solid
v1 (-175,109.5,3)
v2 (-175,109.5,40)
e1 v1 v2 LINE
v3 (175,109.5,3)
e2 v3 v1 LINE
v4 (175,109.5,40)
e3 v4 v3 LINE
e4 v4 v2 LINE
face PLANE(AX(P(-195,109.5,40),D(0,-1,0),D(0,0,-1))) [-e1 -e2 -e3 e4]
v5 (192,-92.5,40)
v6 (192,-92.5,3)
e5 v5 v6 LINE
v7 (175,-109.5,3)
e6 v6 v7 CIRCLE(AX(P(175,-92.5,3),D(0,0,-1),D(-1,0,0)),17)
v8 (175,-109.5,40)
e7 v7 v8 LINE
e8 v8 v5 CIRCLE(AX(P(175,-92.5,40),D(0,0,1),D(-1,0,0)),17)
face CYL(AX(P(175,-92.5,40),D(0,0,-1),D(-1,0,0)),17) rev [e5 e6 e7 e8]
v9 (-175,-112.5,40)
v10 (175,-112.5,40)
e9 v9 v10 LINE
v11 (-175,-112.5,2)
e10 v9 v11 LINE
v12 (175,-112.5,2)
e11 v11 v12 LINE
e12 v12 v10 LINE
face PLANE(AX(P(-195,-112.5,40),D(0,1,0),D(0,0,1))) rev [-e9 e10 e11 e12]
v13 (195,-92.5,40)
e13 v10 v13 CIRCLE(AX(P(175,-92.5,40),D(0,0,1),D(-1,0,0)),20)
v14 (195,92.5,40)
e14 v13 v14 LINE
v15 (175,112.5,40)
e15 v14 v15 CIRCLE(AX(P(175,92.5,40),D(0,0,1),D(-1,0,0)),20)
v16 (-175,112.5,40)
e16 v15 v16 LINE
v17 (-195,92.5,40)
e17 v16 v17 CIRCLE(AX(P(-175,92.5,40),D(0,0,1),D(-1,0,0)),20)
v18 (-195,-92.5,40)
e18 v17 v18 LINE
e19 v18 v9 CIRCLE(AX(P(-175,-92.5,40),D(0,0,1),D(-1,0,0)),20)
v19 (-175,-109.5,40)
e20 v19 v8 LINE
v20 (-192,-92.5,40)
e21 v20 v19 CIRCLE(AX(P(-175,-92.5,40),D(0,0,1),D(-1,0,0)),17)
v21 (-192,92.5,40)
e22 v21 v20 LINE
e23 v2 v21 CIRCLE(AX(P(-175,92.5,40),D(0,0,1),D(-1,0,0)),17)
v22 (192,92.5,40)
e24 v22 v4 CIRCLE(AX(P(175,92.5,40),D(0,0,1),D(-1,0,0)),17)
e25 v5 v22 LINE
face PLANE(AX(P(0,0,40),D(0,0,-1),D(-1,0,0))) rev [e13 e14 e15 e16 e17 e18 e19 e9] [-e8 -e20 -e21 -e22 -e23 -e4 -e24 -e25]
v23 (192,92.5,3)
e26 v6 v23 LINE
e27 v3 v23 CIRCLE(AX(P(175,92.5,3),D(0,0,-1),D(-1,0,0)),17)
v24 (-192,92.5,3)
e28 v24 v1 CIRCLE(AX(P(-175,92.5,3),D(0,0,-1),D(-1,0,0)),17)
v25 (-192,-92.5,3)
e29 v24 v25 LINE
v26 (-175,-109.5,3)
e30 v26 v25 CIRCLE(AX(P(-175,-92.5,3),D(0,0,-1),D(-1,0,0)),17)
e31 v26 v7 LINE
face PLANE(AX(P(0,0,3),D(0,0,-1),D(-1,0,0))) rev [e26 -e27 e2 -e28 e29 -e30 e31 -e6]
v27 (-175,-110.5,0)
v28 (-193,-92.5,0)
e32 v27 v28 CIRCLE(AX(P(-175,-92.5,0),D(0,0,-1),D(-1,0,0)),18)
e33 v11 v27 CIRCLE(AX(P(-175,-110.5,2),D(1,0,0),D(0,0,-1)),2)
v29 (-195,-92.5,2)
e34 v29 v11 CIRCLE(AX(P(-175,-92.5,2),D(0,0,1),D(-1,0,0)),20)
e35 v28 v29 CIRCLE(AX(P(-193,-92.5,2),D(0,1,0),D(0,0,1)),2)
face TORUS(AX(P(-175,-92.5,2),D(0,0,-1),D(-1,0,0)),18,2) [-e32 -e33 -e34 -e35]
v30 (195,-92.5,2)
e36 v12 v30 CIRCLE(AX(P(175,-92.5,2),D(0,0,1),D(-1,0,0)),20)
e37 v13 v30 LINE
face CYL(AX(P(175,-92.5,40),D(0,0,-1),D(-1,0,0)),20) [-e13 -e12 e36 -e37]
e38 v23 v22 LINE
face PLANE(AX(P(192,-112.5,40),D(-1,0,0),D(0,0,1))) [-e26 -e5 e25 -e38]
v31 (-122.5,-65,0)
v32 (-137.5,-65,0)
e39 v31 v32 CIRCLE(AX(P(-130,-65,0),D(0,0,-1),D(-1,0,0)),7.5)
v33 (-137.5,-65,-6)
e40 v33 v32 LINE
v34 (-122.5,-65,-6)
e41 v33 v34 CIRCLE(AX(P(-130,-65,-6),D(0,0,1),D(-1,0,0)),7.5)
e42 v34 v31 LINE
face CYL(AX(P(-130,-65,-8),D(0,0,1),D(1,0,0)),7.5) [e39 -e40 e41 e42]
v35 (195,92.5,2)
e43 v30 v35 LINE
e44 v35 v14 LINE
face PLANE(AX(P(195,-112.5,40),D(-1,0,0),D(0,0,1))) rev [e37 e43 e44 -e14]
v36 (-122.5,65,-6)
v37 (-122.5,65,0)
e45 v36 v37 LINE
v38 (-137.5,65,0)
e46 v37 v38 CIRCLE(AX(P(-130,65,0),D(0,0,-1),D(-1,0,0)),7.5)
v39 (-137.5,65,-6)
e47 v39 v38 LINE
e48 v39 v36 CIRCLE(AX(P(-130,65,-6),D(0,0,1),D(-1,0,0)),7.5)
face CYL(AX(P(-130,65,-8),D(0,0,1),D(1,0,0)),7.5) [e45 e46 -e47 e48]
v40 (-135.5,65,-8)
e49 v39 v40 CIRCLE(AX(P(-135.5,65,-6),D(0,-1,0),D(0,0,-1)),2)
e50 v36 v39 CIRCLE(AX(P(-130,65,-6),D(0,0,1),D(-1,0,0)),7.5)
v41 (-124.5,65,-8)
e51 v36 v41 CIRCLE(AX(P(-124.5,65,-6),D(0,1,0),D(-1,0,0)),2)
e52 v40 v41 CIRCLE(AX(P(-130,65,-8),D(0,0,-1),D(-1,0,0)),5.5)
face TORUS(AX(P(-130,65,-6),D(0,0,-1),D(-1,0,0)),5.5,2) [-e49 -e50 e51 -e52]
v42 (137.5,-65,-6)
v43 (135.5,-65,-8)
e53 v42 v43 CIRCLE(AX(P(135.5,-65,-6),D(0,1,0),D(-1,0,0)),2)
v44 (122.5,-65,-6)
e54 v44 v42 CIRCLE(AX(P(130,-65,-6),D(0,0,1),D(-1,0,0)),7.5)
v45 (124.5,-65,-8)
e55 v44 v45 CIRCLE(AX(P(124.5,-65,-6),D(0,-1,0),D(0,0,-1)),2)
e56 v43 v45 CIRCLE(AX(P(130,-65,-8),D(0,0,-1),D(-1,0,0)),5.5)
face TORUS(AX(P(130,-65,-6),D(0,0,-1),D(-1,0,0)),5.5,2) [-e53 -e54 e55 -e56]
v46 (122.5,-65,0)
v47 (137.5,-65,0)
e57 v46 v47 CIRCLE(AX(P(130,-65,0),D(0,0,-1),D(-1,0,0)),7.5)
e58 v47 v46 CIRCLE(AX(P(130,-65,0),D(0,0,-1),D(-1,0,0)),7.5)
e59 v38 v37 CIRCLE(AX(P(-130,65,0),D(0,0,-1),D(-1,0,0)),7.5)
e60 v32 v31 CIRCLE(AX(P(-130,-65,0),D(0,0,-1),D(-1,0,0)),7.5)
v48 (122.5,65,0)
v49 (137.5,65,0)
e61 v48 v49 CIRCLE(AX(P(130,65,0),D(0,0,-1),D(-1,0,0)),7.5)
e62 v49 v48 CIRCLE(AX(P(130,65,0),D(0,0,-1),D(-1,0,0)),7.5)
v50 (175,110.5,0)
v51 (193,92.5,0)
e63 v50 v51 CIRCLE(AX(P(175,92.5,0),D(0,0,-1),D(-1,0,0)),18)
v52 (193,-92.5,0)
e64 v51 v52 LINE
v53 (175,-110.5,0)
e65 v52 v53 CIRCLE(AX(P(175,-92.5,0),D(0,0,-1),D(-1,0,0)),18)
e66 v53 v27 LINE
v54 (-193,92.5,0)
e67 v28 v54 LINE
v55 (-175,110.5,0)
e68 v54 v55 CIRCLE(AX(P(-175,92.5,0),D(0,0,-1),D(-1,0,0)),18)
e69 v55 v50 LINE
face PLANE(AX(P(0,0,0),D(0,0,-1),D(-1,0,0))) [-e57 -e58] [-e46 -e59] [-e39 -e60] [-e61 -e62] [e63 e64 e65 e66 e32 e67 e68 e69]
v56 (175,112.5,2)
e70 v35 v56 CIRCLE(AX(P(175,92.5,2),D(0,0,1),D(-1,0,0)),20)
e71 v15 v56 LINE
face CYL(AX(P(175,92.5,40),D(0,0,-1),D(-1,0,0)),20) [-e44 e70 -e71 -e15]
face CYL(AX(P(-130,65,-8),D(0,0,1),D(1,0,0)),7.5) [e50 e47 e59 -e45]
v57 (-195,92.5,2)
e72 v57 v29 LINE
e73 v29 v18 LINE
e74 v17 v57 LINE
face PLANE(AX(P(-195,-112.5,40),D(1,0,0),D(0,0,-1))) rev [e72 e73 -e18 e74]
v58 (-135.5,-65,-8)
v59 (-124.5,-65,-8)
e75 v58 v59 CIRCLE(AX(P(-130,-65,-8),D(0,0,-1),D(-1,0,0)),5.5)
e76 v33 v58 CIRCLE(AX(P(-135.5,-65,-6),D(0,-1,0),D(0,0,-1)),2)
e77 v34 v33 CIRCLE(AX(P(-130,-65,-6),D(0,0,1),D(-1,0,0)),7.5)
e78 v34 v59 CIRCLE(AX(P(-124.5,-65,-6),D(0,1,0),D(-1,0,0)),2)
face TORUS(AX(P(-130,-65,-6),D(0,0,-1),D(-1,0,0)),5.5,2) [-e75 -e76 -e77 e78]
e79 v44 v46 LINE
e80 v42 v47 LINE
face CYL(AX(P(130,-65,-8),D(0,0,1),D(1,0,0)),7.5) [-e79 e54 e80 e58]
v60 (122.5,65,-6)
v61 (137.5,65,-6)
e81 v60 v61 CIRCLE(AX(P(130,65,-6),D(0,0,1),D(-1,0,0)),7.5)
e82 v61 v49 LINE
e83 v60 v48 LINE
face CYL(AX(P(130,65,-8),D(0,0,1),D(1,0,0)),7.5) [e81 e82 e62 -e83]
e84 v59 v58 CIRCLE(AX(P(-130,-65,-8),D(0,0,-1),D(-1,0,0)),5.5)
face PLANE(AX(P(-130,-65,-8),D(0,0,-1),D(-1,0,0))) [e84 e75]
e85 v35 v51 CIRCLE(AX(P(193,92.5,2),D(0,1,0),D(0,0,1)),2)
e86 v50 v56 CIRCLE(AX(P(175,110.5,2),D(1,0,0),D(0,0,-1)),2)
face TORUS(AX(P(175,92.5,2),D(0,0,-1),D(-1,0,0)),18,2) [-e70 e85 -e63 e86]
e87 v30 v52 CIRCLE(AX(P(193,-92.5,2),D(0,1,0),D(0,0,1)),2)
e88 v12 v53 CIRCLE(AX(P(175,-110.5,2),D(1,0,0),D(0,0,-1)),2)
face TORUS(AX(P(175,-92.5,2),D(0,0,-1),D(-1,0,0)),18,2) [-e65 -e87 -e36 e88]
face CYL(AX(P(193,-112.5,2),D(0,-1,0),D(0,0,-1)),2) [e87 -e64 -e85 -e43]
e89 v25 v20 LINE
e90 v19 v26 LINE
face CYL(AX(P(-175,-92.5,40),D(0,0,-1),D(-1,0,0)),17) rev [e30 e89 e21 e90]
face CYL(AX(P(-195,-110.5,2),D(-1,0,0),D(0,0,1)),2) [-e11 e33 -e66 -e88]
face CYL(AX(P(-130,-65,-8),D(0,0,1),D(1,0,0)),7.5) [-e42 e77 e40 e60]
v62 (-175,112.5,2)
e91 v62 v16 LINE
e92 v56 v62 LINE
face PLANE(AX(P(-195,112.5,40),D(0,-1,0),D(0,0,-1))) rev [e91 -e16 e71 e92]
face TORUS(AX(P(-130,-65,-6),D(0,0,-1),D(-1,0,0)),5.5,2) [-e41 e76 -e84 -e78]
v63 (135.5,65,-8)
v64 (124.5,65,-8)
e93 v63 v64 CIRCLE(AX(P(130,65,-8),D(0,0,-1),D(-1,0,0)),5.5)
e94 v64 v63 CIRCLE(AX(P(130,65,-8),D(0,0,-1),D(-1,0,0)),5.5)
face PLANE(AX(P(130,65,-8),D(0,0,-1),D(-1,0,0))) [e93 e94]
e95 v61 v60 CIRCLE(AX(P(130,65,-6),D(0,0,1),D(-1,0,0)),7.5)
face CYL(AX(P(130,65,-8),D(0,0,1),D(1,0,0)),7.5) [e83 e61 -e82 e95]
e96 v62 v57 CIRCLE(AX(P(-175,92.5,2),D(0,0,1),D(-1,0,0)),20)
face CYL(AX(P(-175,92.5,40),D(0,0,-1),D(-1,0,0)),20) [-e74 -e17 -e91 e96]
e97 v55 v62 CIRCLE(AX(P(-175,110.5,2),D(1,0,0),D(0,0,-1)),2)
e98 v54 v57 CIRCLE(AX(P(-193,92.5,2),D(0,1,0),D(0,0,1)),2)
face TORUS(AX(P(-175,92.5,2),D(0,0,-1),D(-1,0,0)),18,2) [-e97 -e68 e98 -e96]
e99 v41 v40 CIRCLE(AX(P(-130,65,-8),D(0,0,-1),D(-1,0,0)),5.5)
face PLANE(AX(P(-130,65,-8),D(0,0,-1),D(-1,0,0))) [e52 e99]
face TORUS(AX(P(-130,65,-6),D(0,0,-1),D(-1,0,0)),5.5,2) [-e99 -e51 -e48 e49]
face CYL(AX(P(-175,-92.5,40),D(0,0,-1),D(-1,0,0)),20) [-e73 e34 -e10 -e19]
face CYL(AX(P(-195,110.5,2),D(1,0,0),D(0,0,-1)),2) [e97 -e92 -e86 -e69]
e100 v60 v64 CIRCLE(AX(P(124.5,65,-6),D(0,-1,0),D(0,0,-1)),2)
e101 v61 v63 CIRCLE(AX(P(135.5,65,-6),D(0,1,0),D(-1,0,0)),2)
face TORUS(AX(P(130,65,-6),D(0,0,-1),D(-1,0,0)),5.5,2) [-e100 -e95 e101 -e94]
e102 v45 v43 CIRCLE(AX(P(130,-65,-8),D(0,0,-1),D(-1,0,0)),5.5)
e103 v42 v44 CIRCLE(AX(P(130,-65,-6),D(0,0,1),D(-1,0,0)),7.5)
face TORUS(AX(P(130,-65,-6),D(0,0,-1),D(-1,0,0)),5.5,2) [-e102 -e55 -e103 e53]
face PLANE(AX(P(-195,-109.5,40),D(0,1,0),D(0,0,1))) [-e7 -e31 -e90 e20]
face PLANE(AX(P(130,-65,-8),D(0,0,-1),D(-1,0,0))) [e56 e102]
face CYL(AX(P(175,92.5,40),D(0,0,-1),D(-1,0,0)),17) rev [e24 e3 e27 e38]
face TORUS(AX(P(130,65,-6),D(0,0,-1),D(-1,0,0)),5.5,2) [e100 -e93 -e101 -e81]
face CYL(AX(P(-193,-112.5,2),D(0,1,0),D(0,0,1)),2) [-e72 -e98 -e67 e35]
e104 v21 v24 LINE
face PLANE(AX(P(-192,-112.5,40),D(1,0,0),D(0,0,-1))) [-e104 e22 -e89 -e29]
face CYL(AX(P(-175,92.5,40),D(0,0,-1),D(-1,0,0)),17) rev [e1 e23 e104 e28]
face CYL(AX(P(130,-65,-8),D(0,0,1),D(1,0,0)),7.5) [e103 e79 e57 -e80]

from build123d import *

# Parameters (mm, degrees)
SKETCH_1_W                     = 390
SKETCH_1_H                     = 225
EXTRUDE_1_DEPTH                = 40
FILLET_1_R                     = 20
SHELL_1_T                      = -3
FILLET_2_R                     = 2
SKETCH_2_R                     = 7.5
EXTRUDE_2_DEPTH                = 8
FILLET_3_R                     = 2
PATTERN_LINEAR_1_COUNT         = 2
PATTERN_LINEAR_1_PITCH         = 260
PATTERN_LINEAR_1_COUNT_DIR2    = 2
PATTERN_LINEAR_1_PITCH_DIR2    = 130
FILLET_3_OF_PATTERN_LINEAR_1_R = 2


with BuildPart() as part:
    # 草图1 → 凸台-拉伸1 (new body)
    with BuildSketch(Plane.XY):
        Rectangle(SKETCH_1_W, SKETCH_1_H)
    extrude(amount=EXTRUDE_1_DEPTH)

    # 圆角1
    fillet_1_edges = [part.edges().sort_by_distance(p)[0] for p in [
        (195, -112.5, 20),
        (-195, -112.5, 20),
        (-195, 112.5, 20),
        (195, 112.5, 20),
    ]]
    fillet(fillet_1_edges, radius=FILLET_1_R)

    # 抽壳1
    shell_1_openings = [part.faces().sort_by_distance(p)[0] for p in [
        (0, 0, 40),
    ]]
    offset(amount=SHELL_1_T, openings=shell_1_openings, kind=Kind.INTERSECTION)

    # 圆角2
    fillet_2_edges = [part.edges().sort_by_distance(p)[0] for p in [
        (195, 0, 0),
        (0, -112.5, 0),
        (-195, 0, 0),
        (0, 112.5, 0),
        (-189.142135624, -106.642135624, 0),
        (189.142135624, 106.642135624, 0),
        (-189.142135624, 106.642135624, 0),
        (189.142135624, -106.642135624, 0),
    ]]
    fillet(fillet_2_edges, radius=FILLET_2_R)

    # 草图2 → 凸台-拉伸2 (add)
    with BuildSketch(Plane(origin=(0, 0, 0), x_dir=(-1, 0, 0), z_dir=(0, 0, -1))):
        with Locations((-130, 65)):
            Circle(SKETCH_2_R)
    extrude_2 = extrude(amount=EXTRUDE_2_DEPTH)

    # 圆角3
    fillet_3_edges = [part.edges().sort_by_distance(p)[0] for p in [
        (137.5, 65, -8),
    ]]
    fillet(fillet_3_edges, radius=FILLET_3_R)

    # 阵列(线性)1: Extrude 2 2 × 2
    with Locations(*[(-i * PATTERN_LINEAR_1_PITCH, -j * PATTERN_LINEAR_1_PITCH_DIR2, 0) for i in range(PATTERN_LINEAR_1_COUNT) for j in range(PATTERN_LINEAR_1_COUNT_DIR2) if (i, j) != (0, 0)]):
        add(extrude_2)

    # 圆角3 of 阵列(线性)1
    fillet_3_of_pattern_linear_1_edges = [part.edges().sort_by_distance(p)[0] for p in [
        (137.5, -65, -8),
        (-122.5, 65, -8),
        (-122.5, -65, -8),
    ]]
    fillet(fillet_3_of_pattern_linear_1_edges, radius=FILLET_3_OF_PATTERN_LINEAR_1_R)


solid = part.part
